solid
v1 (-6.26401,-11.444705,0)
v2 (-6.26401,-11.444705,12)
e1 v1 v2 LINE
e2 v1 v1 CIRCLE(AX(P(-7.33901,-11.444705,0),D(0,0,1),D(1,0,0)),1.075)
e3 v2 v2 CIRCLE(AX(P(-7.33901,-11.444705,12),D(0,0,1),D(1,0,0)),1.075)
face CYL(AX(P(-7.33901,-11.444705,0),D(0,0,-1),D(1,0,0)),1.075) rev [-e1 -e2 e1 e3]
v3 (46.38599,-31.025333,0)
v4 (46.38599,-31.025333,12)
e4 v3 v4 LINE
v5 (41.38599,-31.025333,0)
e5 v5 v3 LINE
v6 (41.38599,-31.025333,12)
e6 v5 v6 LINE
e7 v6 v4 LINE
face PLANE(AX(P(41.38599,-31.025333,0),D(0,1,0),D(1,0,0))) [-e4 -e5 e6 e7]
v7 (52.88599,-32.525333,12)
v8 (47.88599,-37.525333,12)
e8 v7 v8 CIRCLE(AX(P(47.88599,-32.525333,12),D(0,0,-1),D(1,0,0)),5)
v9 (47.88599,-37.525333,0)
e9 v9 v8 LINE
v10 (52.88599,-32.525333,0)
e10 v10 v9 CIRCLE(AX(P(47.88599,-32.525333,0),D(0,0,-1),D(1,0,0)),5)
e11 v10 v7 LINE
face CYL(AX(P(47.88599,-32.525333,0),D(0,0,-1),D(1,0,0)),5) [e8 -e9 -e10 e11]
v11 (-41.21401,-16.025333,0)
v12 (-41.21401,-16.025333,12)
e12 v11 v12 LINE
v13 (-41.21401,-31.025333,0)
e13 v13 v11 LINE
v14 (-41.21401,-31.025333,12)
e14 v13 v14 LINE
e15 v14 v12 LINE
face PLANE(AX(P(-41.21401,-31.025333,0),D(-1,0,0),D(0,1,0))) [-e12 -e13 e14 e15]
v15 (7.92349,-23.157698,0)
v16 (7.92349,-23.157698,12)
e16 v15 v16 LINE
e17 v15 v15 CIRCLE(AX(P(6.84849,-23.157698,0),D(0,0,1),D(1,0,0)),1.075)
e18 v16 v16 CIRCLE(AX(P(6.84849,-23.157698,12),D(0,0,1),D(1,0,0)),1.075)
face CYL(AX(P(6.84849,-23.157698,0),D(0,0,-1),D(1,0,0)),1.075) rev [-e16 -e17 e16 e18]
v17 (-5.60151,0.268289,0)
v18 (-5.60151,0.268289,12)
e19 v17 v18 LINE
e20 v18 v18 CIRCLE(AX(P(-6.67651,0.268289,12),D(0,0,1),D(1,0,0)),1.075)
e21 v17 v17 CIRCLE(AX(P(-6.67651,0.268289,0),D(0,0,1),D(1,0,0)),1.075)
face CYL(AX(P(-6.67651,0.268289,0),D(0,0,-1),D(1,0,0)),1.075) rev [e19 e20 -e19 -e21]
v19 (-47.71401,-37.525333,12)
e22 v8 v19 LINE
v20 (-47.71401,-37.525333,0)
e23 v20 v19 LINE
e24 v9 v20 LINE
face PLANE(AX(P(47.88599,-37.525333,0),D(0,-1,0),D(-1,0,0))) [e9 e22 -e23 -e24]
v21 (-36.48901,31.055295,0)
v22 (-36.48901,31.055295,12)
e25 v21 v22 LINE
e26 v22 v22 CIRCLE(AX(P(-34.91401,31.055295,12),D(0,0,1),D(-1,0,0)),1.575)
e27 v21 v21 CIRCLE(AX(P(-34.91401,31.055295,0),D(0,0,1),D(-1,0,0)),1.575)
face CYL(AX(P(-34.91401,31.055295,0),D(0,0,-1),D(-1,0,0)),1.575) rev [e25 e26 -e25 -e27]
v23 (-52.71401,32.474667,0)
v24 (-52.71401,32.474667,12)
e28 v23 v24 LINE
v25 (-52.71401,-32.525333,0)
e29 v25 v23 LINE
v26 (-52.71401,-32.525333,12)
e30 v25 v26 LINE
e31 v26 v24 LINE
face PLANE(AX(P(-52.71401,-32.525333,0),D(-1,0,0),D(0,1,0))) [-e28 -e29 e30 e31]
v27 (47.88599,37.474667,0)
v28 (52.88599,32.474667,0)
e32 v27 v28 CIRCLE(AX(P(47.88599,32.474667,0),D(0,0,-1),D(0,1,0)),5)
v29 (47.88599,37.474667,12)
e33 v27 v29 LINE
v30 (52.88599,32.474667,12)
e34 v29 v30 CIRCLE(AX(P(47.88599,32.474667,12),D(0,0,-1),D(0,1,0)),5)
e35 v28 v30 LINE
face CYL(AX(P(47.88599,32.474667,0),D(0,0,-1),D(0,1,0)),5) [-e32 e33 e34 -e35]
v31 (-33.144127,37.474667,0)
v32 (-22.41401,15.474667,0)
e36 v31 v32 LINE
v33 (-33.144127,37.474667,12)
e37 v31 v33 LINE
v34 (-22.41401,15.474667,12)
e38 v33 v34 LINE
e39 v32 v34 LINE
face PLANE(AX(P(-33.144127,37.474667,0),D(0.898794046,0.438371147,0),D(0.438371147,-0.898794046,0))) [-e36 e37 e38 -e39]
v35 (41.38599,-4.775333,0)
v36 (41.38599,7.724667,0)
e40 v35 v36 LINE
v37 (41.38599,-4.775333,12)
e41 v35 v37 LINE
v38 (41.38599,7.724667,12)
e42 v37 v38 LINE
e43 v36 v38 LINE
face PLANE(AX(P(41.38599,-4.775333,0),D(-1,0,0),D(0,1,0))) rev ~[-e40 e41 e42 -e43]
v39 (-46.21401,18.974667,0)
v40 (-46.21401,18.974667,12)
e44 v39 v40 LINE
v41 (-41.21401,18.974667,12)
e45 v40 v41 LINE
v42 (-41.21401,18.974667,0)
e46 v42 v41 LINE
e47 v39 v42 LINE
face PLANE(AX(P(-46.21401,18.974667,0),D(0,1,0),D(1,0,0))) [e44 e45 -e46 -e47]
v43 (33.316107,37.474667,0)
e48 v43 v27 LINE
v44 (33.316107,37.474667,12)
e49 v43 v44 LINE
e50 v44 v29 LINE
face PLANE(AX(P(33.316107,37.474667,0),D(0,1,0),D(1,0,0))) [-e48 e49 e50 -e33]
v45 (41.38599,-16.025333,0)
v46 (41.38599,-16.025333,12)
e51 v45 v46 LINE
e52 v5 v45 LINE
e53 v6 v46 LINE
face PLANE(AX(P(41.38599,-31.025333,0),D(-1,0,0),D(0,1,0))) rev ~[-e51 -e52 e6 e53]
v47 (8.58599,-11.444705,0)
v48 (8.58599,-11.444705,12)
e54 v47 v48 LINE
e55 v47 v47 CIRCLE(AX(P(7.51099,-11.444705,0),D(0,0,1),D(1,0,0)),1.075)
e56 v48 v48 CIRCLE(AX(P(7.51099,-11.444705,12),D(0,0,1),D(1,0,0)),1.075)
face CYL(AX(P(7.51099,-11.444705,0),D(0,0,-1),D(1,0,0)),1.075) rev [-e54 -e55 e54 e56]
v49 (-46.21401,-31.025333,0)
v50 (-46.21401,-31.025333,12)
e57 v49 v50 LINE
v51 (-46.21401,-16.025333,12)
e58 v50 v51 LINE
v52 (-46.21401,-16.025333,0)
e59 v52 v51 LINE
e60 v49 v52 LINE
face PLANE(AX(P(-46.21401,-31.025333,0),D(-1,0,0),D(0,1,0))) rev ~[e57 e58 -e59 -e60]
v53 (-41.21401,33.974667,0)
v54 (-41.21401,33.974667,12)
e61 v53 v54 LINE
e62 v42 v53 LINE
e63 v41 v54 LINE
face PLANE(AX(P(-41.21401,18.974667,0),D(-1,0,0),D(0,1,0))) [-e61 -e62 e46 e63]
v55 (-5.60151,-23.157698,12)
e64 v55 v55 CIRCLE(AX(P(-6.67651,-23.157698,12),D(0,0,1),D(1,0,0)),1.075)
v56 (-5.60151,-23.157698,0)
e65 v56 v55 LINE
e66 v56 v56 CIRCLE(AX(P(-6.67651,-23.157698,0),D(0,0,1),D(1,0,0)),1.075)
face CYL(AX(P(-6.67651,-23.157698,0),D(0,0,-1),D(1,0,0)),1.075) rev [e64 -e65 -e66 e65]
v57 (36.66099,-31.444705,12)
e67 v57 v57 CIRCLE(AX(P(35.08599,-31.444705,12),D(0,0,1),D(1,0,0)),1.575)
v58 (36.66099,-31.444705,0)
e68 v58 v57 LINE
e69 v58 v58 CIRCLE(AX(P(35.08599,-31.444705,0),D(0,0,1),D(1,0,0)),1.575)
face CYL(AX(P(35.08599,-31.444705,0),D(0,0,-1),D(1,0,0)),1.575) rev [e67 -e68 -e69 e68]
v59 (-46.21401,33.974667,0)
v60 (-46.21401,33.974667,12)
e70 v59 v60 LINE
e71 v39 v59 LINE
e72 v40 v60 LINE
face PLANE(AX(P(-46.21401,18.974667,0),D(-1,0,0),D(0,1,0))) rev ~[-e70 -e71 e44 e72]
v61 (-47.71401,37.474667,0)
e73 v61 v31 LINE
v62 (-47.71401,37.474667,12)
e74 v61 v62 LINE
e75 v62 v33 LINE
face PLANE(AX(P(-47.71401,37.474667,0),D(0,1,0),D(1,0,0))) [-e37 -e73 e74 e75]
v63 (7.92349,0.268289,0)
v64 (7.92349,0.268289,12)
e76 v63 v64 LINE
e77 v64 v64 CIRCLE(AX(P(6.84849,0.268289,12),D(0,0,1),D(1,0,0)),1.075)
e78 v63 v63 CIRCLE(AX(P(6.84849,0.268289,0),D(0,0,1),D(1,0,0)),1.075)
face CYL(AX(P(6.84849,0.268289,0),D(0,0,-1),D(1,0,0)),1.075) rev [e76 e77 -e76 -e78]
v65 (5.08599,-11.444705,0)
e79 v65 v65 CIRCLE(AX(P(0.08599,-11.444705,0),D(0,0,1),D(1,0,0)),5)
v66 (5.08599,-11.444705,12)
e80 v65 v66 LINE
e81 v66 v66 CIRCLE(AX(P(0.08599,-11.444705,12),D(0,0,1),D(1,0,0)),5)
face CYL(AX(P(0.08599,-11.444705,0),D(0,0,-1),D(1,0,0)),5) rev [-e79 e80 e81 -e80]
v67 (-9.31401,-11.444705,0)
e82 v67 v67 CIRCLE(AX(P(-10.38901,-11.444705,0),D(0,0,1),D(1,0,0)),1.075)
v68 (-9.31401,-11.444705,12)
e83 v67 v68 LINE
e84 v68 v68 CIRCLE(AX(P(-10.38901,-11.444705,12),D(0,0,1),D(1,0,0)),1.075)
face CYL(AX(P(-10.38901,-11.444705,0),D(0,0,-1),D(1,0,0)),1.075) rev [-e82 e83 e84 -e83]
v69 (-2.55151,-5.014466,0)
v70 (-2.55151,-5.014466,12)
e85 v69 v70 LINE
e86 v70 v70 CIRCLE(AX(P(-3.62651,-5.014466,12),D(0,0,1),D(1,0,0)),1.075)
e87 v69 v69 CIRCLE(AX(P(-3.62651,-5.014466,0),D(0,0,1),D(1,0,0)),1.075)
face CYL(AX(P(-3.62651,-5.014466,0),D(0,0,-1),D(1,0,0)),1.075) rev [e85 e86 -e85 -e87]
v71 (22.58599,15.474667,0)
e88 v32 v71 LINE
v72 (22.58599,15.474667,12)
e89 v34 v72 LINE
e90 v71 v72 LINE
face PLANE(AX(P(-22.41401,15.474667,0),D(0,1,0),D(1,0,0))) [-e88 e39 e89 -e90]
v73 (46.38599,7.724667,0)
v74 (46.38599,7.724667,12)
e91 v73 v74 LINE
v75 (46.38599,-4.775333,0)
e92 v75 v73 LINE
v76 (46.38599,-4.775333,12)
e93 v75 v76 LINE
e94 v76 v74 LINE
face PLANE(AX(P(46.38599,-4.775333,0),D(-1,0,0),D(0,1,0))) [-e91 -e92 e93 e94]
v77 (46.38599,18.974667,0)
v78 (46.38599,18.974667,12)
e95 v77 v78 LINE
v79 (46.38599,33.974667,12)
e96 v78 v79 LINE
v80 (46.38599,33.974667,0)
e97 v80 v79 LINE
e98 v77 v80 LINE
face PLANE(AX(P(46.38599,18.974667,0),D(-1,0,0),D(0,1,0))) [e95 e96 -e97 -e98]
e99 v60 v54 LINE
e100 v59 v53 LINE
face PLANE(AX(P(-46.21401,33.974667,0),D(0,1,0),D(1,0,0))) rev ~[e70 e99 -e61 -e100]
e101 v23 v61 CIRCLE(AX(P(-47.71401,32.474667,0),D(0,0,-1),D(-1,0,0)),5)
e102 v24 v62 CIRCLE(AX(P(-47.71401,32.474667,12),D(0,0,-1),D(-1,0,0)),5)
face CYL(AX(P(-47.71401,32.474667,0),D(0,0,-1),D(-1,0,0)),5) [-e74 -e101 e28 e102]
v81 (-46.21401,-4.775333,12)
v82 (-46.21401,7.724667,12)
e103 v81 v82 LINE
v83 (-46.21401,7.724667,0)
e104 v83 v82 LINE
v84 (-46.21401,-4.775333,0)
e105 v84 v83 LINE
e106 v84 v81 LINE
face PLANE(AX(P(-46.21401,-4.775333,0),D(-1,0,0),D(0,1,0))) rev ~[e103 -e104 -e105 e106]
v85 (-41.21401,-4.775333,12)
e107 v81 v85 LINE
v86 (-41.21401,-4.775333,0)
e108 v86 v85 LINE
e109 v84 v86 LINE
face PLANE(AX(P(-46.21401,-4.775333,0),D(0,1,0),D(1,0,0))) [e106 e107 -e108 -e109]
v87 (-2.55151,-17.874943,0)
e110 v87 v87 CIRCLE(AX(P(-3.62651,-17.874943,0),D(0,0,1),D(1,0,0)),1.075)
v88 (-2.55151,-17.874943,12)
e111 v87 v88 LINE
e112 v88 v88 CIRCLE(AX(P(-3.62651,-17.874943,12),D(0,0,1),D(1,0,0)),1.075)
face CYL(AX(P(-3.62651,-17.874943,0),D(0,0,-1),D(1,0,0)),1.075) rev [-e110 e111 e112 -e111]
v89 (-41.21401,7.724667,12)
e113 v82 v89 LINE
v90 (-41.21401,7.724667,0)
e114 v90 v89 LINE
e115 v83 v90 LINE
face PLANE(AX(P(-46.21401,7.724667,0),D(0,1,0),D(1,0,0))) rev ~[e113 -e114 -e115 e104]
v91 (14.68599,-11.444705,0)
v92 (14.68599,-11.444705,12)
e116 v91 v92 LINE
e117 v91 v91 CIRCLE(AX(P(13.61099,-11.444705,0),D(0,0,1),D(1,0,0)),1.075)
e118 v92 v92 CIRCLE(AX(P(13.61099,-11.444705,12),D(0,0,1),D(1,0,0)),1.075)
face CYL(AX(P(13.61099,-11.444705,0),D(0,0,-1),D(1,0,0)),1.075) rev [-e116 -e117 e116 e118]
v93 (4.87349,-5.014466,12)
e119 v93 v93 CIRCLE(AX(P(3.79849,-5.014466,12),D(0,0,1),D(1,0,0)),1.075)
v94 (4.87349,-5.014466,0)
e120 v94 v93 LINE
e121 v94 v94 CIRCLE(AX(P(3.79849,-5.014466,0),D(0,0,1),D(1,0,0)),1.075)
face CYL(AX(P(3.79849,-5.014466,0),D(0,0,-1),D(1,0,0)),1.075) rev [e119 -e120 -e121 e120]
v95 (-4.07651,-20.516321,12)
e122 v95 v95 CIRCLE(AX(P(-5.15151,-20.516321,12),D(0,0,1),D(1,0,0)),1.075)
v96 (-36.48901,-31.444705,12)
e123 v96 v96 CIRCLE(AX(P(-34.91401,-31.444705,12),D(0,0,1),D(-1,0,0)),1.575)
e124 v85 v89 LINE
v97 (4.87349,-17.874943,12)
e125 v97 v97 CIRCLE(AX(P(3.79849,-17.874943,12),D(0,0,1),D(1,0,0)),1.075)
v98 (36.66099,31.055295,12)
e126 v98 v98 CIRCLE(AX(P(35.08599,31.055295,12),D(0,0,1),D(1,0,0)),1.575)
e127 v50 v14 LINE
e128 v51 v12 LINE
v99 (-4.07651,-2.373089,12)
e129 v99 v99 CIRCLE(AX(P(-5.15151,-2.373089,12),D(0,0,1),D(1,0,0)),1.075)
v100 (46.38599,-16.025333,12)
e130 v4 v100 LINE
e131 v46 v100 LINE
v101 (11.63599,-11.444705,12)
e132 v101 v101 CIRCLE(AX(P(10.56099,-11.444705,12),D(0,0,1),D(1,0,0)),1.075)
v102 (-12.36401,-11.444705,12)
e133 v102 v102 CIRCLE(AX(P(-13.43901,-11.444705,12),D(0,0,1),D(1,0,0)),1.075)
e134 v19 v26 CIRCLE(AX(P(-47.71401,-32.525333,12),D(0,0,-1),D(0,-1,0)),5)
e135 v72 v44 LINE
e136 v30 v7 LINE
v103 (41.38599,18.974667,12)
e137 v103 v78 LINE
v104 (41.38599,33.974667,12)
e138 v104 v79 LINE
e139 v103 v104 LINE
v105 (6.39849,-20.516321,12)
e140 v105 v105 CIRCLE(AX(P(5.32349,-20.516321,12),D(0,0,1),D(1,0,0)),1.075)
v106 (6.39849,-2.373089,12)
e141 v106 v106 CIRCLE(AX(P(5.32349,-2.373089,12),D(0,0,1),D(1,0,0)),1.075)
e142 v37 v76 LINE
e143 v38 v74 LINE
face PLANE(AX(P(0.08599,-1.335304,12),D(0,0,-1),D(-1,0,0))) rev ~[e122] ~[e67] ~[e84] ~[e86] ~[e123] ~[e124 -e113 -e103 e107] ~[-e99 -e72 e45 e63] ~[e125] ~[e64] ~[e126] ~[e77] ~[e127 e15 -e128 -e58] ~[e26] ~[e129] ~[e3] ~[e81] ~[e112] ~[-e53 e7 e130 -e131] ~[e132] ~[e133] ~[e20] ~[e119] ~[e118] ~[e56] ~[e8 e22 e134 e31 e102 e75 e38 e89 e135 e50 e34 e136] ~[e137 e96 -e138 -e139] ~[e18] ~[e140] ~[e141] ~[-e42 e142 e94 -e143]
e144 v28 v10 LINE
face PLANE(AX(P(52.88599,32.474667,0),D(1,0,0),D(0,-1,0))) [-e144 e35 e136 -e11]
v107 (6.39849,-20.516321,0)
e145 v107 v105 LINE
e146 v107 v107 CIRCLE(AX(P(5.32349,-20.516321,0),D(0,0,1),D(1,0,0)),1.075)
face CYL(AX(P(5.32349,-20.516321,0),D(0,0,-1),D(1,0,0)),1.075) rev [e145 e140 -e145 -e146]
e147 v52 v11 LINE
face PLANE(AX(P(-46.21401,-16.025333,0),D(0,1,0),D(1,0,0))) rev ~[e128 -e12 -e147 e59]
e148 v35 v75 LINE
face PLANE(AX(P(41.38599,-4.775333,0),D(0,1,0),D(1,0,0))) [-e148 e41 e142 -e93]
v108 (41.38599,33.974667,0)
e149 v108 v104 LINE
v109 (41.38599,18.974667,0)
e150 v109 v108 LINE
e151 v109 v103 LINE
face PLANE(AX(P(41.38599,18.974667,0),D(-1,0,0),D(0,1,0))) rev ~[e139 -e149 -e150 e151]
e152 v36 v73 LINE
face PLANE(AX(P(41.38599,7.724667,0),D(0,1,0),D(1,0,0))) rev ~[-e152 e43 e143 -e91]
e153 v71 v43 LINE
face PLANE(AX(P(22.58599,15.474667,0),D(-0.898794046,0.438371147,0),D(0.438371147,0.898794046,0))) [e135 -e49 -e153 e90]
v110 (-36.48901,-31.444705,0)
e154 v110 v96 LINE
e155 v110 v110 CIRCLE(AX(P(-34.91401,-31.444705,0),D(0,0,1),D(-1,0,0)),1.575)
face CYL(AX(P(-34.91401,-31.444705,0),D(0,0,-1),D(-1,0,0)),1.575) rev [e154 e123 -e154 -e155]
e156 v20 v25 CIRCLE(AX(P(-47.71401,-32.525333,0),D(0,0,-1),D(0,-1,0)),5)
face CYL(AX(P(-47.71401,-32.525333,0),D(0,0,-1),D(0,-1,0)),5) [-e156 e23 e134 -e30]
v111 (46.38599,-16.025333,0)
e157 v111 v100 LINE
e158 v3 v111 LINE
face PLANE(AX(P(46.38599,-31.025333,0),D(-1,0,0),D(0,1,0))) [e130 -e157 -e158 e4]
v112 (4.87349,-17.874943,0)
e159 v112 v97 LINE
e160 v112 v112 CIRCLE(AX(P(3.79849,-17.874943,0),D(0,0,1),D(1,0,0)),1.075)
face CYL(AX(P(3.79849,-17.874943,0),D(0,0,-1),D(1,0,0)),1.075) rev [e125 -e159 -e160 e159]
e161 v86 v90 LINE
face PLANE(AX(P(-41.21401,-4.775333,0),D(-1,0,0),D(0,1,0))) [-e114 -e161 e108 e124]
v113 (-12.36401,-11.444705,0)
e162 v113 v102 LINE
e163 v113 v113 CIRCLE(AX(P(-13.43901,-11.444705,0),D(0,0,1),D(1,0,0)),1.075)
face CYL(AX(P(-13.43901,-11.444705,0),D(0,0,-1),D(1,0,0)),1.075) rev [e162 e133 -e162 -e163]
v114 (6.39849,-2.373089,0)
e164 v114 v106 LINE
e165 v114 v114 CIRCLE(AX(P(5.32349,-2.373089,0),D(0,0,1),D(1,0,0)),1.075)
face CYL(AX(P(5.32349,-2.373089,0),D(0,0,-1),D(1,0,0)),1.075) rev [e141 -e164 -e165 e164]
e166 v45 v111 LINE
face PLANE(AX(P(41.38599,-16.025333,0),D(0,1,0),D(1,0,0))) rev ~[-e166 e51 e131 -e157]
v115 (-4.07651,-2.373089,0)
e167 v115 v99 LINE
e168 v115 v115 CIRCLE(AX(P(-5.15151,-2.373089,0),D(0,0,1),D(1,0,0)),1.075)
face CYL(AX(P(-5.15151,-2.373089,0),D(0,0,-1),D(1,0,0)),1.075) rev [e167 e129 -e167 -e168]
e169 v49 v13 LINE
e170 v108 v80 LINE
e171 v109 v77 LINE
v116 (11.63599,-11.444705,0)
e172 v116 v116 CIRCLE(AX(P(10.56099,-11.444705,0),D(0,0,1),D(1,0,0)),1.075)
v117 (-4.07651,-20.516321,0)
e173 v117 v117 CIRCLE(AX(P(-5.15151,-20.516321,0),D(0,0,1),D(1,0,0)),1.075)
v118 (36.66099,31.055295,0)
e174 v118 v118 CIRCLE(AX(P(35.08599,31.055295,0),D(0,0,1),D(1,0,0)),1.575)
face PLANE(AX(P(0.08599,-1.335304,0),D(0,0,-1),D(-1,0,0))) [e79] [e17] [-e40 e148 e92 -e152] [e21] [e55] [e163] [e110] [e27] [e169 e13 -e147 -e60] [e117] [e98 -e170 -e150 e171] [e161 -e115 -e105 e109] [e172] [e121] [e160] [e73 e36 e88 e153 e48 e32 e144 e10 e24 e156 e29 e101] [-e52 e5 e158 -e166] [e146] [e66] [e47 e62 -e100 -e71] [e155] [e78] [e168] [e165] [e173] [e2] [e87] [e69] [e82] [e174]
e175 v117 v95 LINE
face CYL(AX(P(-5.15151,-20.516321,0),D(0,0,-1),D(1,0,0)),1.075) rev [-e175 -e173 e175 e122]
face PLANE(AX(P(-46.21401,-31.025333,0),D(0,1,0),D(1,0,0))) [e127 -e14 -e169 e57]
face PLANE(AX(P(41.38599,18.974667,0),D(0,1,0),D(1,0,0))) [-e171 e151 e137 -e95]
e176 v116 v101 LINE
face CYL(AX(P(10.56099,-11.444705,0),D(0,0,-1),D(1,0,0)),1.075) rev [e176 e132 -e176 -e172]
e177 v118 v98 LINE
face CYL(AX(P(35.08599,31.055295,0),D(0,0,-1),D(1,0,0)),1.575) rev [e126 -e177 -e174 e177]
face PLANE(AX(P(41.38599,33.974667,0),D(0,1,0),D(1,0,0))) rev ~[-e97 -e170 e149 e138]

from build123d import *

# Parameters (mm, degrees)
SKETCH_1_R      = 1.575
SKETCH_1_R_2    = 5
SKETCH_1_R_3    = 1.075
SKETCH_1_W      = 5
SKETCH_1_H      = 15
SKETCH_1_H_2    = 12.5
EXTRUDE_1_DEPTH = 12


with BuildPart() as part:
    # 草图1 → 凸台-拉伸1 (new body)
    with BuildSketch(Plane.XY):
        with BuildLine():
            Line((-33.144127259, 37.474667316), (-22.414010311, 15.474667316))
            Line((-22.414010311, 15.474667316), (22.585989689, 15.474667316))
            Line((22.585989689, 15.474667316), (33.316106638, 37.474667316))
            Line((33.316106638, 37.474667316), (47.885989689, 37.474667316))
            ThreePointArc((47.885989689, 37.474667316), (51.421523595, 36.010201222), (52.885989689, 32.474667316))
            Line((52.885989689, 32.474667316), (52.885989689, -32.525332684))
            ThreePointArc((52.885989689, -32.525332684), (51.421523595, -36.060866589), (47.885989689, -37.525332684))
            Line((47.885989689, -37.525332684), (-47.714010311, -37.525332684))
            ThreePointArc((-47.714010311, -37.525332684), (-51.249544217, -36.060866589), (-52.714010311, -32.525332684))
            Line((-52.714010311, -32.525332684), (-52.714010311, 32.474667316))
            ThreePointArc((-52.714010311, 32.474667316), (-51.249544217, 36.010201222), (-47.714010311, 37.474667316))
            Line((-47.714010311, 37.474667316), (-33.144127259, 37.474667316))
        make_face()
        with Locations((35.085989689, 31.055295289)):
            Circle(SKETCH_1_R, mode=Mode.SUBTRACT)
        with Locations((35.085989689, -31.444704711)):
            Circle(SKETCH_1_R, mode=Mode.SUBTRACT)
        with Locations((0.085989689, -11.444704711)):
            Circle(SKETCH_1_R_2, mode=Mode.SUBTRACT)
        with Locations((7.510989689, -11.444704711)):
            Circle(SKETCH_1_R_3, mode=Mode.SUBTRACT)
        with Locations((10.560989689, -11.444704711)):
            Circle(SKETCH_1_R_3, mode=Mode.SUBTRACT)
        with Locations((13.610989689, -11.444704711)):
            Circle(SKETCH_1_R_3, mode=Mode.SUBTRACT)
        with Locations((5.323489689, -20.516320815)):
            Circle(SKETCH_1_R_3, mode=Mode.SUBTRACT)
        with Locations((3.798489689, -17.874943334)):
            Circle(SKETCH_1_R_3, mode=Mode.SUBTRACT)
        with Locations((6.848489689, -23.157698297)):
            Circle(SKETCH_1_R_3, mode=Mode.SUBTRACT)
        with Locations((-5.151510311, -20.516320815)):
            Circle(SKETCH_1_R_3, mode=Mode.SUBTRACT)
        with Locations((-3.626510311, -17.874943334)):
            Circle(SKETCH_1_R_3, mode=Mode.SUBTRACT)
        with Locations((-6.676510311, -23.157698297)):
            Circle(SKETCH_1_R_3, mode=Mode.SUBTRACT)
        with Locations((-10.389010311, -11.444704711)):
            Circle(SKETCH_1_R_3, mode=Mode.SUBTRACT)
        with Locations((-7.339010311, -11.444704711)):
            Circle(SKETCH_1_R_3, mode=Mode.SUBTRACT)
        with Locations((-13.439010311, -11.444704711)):
            Circle(SKETCH_1_R_3, mode=Mode.SUBTRACT)
        with Locations((-5.151510311, -2.373088606)):
            Circle(SKETCH_1_R_3, mode=Mode.SUBTRACT)
        with Locations((-3.626510311, -5.014466088)):
            Circle(SKETCH_1_R_3, mode=Mode.SUBTRACT)
        with Locations((-6.676510311, 0.268288875)):
            Circle(SKETCH_1_R_3, mode=Mode.SUBTRACT)
        with Locations((5.323489689, -2.373088606)):
            Circle(SKETCH_1_R_3, mode=Mode.SUBTRACT)
        with Locations((3.798489689, -5.014466088)):
            Circle(SKETCH_1_R_3, mode=Mode.SUBTRACT)
        with Locations((6.848489689, 0.268288875)):
            Circle(SKETCH_1_R_3, mode=Mode.SUBTRACT)
        with Locations(Location((-34.914010311, 31.055295289, 0), (0, 0, 180))):
            Circle(SKETCH_1_R, mode=Mode.SUBTRACT)
        with Locations(Location((-34.914010311, -31.444704711, 0), (0, 0, 180))):
            Circle(SKETCH_1_R, mode=Mode.SUBTRACT)
        with Locations((-43.714010311, -23.525332684)):
            Rectangle(SKETCH_1_W, SKETCH_1_H, mode=Mode.SUBTRACT)
        with Locations((43.885989689, -23.525332684)):
            Rectangle(SKETCH_1_W, SKETCH_1_H, mode=Mode.SUBTRACT)
        with Locations((43.885989689, 1.474667316)):
            Rectangle(SKETCH_1_W, SKETCH_1_H_2, mode=Mode.SUBTRACT)
        with Locations((43.885989689, 26.474667316)):
            Rectangle(SKETCH_1_W, SKETCH_1_H, mode=Mode.SUBTRACT)
        with Locations((-43.714010311, 1.474667316)):
            Rectangle(SKETCH_1_W, SKETCH_1_H_2, mode=Mode.SUBTRACT)
        with Locations((-43.714010311, 26.474667316)):
            Rectangle(SKETCH_1_W, SKETCH_1_H, mode=Mode.SUBTRACT)
    extrude(amount=EXTRUDE_1_DEPTH)


solid = part.part
